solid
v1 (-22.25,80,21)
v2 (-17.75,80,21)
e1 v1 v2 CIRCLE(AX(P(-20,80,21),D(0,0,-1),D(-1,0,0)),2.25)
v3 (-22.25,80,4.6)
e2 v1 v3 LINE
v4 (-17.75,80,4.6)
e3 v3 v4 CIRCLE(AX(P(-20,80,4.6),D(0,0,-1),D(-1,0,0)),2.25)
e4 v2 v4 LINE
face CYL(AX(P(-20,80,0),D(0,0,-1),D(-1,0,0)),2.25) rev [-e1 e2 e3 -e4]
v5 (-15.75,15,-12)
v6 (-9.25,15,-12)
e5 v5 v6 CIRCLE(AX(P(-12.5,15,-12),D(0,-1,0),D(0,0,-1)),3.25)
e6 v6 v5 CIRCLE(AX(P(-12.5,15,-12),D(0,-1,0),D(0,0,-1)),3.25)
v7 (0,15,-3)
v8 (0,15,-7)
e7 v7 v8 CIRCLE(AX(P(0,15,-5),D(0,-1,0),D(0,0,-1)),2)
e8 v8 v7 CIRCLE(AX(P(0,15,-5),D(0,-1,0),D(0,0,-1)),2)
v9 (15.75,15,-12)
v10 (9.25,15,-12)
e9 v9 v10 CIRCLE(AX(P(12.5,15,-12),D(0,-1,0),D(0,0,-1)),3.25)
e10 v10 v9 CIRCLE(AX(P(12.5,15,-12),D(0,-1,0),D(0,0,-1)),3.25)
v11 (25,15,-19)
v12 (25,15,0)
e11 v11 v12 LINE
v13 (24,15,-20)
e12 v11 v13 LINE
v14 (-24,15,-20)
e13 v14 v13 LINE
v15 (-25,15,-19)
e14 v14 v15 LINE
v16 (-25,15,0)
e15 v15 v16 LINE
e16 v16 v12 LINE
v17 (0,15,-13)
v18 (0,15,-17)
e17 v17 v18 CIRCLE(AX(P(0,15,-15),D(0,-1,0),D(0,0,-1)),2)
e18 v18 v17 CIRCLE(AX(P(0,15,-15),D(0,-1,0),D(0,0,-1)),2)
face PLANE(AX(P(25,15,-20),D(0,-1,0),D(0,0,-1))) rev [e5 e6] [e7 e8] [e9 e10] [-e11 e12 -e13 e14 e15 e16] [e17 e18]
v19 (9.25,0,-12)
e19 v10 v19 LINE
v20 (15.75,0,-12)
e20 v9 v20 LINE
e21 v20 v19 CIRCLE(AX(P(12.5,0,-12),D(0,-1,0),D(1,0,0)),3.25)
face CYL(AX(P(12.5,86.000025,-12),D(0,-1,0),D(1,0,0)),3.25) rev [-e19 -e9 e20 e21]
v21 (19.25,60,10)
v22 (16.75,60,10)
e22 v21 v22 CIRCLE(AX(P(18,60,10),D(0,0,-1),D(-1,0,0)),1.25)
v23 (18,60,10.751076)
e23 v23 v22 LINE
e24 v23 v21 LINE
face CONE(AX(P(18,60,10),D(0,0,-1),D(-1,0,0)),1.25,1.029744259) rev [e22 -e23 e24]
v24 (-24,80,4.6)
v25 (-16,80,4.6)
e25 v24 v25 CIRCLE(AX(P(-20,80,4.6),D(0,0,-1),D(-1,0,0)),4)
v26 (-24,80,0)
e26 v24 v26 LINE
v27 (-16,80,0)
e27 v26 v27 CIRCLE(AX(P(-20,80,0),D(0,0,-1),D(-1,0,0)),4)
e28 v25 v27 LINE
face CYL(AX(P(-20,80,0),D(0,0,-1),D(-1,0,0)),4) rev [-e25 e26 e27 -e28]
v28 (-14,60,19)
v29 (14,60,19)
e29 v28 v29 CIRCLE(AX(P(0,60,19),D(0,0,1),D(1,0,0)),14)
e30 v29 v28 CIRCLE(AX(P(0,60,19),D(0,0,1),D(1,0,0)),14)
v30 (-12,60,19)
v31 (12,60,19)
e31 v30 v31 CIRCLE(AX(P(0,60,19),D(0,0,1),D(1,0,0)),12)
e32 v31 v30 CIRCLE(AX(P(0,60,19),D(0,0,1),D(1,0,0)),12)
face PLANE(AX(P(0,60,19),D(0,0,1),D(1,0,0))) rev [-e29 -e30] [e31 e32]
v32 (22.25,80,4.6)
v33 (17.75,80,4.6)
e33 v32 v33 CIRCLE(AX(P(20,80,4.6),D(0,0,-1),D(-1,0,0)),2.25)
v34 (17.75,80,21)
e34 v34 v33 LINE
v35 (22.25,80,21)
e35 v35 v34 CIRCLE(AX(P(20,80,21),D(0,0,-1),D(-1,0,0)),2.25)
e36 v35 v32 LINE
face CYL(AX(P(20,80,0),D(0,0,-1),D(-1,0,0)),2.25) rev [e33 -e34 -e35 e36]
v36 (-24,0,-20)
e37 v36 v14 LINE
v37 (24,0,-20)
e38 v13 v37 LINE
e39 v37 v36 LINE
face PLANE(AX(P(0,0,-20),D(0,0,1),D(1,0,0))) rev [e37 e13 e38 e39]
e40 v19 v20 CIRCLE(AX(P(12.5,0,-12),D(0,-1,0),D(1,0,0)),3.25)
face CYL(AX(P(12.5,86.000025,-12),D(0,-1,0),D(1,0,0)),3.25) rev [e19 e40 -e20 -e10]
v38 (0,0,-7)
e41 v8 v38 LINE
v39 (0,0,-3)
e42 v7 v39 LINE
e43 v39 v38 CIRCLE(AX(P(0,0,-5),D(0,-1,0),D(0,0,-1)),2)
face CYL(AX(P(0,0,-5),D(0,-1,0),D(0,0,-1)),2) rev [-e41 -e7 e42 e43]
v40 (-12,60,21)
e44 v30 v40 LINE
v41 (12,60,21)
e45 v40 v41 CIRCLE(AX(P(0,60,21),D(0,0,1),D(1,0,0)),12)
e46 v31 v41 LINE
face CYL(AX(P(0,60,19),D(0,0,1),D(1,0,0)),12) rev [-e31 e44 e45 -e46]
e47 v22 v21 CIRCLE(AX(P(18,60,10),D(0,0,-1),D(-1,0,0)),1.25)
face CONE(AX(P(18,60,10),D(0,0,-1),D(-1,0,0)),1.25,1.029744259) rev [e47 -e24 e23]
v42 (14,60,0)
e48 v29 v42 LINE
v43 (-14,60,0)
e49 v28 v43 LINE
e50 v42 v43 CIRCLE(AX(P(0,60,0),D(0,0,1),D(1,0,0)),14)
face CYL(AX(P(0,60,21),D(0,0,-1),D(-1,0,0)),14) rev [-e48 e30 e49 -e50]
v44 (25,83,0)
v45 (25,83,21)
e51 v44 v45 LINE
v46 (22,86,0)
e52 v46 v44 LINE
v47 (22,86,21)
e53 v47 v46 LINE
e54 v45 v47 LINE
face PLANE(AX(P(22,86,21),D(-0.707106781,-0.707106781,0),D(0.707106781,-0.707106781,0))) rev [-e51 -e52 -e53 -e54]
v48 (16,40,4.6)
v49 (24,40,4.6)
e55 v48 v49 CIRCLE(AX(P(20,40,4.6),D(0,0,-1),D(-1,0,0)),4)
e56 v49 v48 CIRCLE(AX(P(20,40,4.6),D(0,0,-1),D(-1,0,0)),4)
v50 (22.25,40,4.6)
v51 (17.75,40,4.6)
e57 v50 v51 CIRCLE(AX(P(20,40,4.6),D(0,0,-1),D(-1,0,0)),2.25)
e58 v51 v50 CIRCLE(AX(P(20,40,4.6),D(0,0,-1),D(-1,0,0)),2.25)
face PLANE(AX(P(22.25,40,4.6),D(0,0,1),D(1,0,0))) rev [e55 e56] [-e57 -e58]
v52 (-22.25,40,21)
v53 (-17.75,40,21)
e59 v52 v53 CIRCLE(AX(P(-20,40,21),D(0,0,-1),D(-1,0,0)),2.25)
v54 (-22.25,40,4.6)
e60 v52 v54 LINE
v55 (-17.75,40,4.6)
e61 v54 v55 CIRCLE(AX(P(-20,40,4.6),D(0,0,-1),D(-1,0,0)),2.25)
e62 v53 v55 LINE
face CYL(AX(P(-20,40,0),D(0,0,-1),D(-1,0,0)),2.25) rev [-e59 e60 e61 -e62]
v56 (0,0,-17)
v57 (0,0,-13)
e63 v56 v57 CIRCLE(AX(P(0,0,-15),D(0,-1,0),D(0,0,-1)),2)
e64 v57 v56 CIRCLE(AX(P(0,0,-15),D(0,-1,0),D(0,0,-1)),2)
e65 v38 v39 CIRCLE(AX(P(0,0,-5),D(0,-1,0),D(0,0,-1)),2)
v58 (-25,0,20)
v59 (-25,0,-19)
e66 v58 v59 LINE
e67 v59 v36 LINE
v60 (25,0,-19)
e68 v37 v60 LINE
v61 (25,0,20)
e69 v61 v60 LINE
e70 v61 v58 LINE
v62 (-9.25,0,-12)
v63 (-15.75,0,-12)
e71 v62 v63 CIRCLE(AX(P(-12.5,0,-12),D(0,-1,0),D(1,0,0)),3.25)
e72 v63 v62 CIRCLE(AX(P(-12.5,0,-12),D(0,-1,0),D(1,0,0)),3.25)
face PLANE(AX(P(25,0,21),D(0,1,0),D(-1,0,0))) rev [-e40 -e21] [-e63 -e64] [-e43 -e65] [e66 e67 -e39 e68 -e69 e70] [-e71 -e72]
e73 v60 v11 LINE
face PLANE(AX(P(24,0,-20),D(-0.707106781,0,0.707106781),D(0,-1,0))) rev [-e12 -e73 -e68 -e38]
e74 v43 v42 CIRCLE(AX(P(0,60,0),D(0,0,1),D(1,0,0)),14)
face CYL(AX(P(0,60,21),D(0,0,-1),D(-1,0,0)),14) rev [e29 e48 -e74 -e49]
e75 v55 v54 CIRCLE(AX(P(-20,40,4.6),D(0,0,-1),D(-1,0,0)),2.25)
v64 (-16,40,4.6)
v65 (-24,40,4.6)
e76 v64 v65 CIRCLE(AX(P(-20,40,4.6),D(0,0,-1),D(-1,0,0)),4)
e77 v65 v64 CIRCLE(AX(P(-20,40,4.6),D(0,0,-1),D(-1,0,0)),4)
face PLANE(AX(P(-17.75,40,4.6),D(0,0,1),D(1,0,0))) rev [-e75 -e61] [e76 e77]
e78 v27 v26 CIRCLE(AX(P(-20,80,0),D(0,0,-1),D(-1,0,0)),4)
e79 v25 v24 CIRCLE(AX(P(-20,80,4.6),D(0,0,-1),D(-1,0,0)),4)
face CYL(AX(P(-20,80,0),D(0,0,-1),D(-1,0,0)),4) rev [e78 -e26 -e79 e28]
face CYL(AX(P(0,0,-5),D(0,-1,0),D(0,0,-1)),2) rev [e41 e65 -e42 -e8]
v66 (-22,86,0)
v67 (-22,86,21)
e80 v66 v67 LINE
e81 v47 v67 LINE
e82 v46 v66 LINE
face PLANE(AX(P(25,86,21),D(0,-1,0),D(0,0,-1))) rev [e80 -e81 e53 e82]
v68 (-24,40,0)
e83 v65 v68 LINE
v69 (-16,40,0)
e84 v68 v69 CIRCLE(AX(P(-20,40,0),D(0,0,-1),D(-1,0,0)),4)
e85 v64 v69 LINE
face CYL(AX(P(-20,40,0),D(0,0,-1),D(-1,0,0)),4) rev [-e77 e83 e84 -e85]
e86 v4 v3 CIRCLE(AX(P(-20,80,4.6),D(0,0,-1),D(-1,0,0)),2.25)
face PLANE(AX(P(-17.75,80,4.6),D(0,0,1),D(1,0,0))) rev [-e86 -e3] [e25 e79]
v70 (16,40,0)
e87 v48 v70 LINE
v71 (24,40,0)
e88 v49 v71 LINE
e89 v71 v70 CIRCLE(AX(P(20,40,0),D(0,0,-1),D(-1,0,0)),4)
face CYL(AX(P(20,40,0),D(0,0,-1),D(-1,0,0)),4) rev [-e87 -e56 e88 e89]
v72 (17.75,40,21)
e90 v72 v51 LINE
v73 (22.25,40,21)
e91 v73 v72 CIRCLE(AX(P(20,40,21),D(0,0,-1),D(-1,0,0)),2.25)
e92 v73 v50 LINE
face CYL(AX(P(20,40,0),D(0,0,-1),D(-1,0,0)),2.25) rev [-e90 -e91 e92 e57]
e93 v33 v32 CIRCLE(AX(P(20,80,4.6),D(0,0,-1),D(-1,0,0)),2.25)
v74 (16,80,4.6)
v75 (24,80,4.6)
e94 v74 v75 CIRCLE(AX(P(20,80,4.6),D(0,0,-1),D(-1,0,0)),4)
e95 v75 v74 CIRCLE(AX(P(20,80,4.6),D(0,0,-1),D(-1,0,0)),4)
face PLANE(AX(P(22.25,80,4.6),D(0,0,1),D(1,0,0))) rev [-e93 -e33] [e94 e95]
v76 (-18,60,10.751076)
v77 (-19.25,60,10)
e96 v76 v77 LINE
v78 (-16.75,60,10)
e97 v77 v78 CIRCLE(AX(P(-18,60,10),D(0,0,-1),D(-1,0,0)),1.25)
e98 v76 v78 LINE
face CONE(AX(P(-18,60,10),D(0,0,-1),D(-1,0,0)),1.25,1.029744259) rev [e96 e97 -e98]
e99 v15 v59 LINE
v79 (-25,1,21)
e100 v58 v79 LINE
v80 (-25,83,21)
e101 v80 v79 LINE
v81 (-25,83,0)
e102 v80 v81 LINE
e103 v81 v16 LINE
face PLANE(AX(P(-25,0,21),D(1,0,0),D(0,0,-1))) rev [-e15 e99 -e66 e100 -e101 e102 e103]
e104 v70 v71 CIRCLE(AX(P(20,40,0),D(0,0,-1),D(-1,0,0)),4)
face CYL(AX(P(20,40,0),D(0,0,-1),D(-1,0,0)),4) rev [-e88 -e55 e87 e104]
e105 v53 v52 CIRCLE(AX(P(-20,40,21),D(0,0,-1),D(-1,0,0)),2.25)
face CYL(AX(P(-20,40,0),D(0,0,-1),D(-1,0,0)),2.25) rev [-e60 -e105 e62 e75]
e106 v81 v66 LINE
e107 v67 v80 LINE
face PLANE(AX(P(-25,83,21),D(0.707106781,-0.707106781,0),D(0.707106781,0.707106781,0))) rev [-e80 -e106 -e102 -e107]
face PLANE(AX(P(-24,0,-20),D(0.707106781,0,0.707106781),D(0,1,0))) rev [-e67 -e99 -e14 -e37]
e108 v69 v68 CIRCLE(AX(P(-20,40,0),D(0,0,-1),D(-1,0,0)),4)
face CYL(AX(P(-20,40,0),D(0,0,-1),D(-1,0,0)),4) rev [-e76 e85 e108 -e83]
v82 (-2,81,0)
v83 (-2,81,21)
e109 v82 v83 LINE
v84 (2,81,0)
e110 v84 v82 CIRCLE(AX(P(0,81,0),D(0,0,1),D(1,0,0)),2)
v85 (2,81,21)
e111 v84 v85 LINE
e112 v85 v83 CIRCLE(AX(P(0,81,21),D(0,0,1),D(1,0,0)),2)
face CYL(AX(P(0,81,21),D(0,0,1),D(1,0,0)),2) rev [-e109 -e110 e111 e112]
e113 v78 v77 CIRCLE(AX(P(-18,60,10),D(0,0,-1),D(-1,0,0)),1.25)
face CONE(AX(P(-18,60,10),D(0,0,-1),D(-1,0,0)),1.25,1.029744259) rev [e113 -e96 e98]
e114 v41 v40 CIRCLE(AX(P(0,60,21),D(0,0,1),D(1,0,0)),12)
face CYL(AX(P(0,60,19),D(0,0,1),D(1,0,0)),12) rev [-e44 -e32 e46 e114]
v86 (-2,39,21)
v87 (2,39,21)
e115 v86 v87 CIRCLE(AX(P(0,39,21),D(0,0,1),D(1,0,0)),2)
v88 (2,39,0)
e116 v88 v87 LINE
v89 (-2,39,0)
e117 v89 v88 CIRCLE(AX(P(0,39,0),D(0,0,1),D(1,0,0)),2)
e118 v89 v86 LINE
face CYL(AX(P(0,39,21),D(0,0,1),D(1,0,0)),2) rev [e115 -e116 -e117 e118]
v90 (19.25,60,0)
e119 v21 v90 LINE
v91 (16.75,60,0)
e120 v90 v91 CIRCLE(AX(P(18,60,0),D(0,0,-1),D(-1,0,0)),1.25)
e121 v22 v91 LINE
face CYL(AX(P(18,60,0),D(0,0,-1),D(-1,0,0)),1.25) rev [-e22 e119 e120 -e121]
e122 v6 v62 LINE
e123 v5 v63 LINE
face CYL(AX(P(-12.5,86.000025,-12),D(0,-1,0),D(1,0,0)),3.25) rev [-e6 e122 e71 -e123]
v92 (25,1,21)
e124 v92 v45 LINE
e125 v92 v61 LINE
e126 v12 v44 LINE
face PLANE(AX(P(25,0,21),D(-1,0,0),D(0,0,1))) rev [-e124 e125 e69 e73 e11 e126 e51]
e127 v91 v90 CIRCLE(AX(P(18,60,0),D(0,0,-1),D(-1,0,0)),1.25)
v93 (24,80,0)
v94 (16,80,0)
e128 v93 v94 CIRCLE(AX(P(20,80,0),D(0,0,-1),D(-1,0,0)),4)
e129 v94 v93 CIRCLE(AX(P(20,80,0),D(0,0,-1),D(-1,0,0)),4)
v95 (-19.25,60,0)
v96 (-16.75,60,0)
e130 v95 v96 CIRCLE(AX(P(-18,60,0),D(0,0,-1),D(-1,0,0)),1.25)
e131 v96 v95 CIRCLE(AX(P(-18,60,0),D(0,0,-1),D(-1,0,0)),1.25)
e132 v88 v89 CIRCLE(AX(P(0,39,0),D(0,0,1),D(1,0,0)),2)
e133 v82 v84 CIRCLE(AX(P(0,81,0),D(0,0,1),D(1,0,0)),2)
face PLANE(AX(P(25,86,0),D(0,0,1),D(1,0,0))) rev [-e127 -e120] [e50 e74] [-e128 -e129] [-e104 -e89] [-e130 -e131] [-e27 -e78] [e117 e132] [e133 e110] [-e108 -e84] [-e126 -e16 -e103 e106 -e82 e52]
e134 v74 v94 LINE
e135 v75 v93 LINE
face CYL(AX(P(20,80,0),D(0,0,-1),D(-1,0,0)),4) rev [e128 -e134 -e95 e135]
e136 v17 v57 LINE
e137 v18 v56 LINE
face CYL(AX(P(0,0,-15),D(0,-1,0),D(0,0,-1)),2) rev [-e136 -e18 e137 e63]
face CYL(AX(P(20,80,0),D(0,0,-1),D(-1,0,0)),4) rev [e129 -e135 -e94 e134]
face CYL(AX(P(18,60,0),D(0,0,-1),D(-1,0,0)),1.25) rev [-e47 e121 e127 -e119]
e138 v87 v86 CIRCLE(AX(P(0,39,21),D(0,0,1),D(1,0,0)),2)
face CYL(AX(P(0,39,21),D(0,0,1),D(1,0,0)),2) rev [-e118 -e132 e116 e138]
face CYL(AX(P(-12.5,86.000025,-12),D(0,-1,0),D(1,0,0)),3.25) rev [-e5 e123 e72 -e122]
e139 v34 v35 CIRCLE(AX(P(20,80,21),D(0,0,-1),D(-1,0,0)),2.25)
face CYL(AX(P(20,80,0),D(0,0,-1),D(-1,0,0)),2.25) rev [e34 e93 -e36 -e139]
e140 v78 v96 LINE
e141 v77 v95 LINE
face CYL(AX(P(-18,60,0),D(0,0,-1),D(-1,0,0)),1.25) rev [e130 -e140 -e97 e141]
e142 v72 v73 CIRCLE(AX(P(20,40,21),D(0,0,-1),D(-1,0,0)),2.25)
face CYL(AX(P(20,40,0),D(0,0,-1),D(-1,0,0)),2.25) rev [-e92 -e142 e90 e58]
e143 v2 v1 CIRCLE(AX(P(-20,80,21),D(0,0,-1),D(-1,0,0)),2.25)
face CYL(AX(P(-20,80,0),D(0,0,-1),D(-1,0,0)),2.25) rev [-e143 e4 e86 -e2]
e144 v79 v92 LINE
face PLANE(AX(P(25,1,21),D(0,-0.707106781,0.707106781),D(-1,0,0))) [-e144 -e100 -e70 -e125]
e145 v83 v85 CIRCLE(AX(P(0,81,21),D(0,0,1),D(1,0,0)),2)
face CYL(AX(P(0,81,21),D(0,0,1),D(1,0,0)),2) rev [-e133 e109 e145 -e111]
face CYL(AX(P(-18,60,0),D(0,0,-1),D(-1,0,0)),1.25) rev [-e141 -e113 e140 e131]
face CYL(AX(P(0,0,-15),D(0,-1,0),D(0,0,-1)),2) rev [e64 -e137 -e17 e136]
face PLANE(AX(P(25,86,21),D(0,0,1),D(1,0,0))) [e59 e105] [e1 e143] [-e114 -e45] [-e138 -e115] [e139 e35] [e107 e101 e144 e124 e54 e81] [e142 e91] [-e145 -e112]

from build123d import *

# Parameters (mm, degrees)
SKETCH3_W                                            = 50
SKETCH3_H                                            = 86
SKETCH3_R                                            = 14
BOSS_EXTRUDE1_DEPTH                                  = 21
M3_TAPPED_HOLE1_D                                    = 2.5
M3_TAPPED_HOLE1_DEPTH                                = 10
M3_TAPPED_HOLE1_TIP                                  = 0.751075774
BOSS_EXTRUDE3_START                                  = -2
SKETCH4_R                                            = 14
SKETCH4_R_2                                          = 12
BOSS_EXTRUDE3_DEPTH                                  = 2
F_4_0_4_DIAMETER_HOLE2_D                             = 4
SKETCH22_W                                           = 50
SKETCH22_H                                           = 15
BOSS_EXTRUDE5_DEPTH                                  = 20
SKETCH23_R                                           = 3.25
CUT_EXTRUDE3_DEPTH                                   = 92.989129793
F_4_0_4_DIAMETER_HOLE1_D                             = 4
F_4_0_4_DIAMETER_HOLE1_DEPTH                         = 15
F_4_0_4_DIAMETER_HOLE1_TIP                           = 1.201721238
HOLE_SIZE_PER_SOCKET_HEAD_CAP_SCREW_TYPE_D           = 4.5
HOLE_SIZE_PER_SOCKET_HEAD_CAP_SCREW_TYPE_CBORE_D     = 8
HOLE_SIZE_PER_SOCKET_HEAD_CAP_SCREW_TYPE_CBORE_DEPTH = 4.6
CHAMFER1_SIZE                                        = 3
CHAMFER2_SIZE                                        = 1


with BuildPart() as part:
    # Sketch3 → Boss-Extrude1 (new body)
    with BuildSketch(Plane.XY):
        with Locations((0, 43)):
            Rectangle(SKETCH3_W, SKETCH3_H)
        with Locations(Location((0, 60, 0), (0, 0, 180))):
            Circle(SKETCH3_R, mode=Mode.SUBTRACT)
    extrude(amount=BOSS_EXTRUDE1_DEPTH)

    # M3 Tapped Hole1
    with Locations(Plane(origin=(6.398868237, 17.925711715, 0), x_dir=(1, 0, 0), z_dir=(0, 0, -1))):
        with Locations((11.601131763, -42.074288285), (-24.398868237, -42.074288285)):
            Hole(M3_TAPPED_HOLE1_D / 2, depth=M3_TAPPED_HOLE1_DEPTH)
            with Locations((0, 0, -(M3_TAPPED_HOLE1_DEPTH + M3_TAPPED_HOLE1_TIP / 2))):  # 118° drill point
                Cone(0, M3_TAPPED_HOLE1_D / 2, M3_TAPPED_HOLE1_TIP, mode=Mode.SUBTRACT)

    # Sketch4 → Boss-Extrude3 (add)
    with BuildSketch(Plane.XY.offset(21).offset(BOSS_EXTRUDE3_START)):
        with Locations(Location((0, 60, 0), (0, 0, 180))):
            Circle(SKETCH4_R)
        with Locations((0, 60)):
            Circle(SKETCH4_R_2, mode=Mode.SUBTRACT)
    extrude(amount=BOSS_EXTRUDE3_DEPTH)

    # Ø4.0 (4) Diameter Hole2 (through all)
    with Locations(Plane.XY.offset(21)):
        with Locations((0, 81), (0, 39)):
            Hole(F_4_0_4_DIAMETER_HOLE2_D / 2)

    # Sketch22 → Boss-Extrude5 (add)
    with BuildSketch(Plane(origin=(0, 0, 0), x_dir=(-1, 0, 0), z_dir=(0, 0, -1))):
        with Locations((0, 7.5)):
            Rectangle(SKETCH22_W, SKETCH22_H)
    extrude(amount=BOSS_EXTRUDE5_DEPTH)

    # Sketch23 → Cut-Extrude3 (cut, through all)
    with BuildSketch(Plane.XZ):
        with Locations((12.5, -12)):
            Circle(SKETCH23_R)
        with Locations((-12.5, -12)):
            Circle(SKETCH23_R)
    extrude(amount=-CUT_EXTRUDE3_DEPTH, mode=Mode.SUBTRACT)

    # Ø4.0 (4) Diameter Hole1
    with Locations(Plane.XZ):
        with Locations((0, -15), (0, -5)):
            Hole(F_4_0_4_DIAMETER_HOLE1_D / 2, depth=F_4_0_4_DIAMETER_HOLE1_DEPTH)
            with Locations((0, 0, -(F_4_0_4_DIAMETER_HOLE1_DEPTH + F_4_0_4_DIAMETER_HOLE1_TIP / 2))):  # 118° drill point
                Cone(0, F_4_0_4_DIAMETER_HOLE1_D / 2, F_4_0_4_DIAMETER_HOLE1_TIP, mode=Mode.SUBTRACT)

    # Hole size per socket head cap screw type 1 (through all)
    with Locations(Plane(origin=(0, 0, 0), x_dir=(-1, 0, 0), z_dir=(0, 0, -1))):
        with Locations((-20, 80), (-20, 40), (20, 40), (20, 80)):
            CounterBoreHole(HOLE_SIZE_PER_SOCKET_HEAD_CAP_SCREW_TYPE_D / 2, HOLE_SIZE_PER_SOCKET_HEAD_CAP_SCREW_TYPE_CBORE_D / 2, HOLE_SIZE_PER_SOCKET_HEAD_CAP_SCREW_TYPE_CBORE_DEPTH)

    # Chamfer1
    chamfer1_edges = [part.edges().sort_by_distance(p)[0] for p in [
        (-25, 86, 10.5),
        (25, 86, 10.5),
    ]]
    chamfer(chamfer1_edges, length=CHAMFER1_SIZE)

    # Chamfer2
    chamfer2_edges = [part.edges().sort_by_distance(p)[0] for p in [
        (0, 0, 21),
        (25, 7.5, -20),
        (-25, 7.5, -20),
    ]]
    chamfer(chamfer2_edges, length=CHAMFER2_SIZE)


solid = part.part
